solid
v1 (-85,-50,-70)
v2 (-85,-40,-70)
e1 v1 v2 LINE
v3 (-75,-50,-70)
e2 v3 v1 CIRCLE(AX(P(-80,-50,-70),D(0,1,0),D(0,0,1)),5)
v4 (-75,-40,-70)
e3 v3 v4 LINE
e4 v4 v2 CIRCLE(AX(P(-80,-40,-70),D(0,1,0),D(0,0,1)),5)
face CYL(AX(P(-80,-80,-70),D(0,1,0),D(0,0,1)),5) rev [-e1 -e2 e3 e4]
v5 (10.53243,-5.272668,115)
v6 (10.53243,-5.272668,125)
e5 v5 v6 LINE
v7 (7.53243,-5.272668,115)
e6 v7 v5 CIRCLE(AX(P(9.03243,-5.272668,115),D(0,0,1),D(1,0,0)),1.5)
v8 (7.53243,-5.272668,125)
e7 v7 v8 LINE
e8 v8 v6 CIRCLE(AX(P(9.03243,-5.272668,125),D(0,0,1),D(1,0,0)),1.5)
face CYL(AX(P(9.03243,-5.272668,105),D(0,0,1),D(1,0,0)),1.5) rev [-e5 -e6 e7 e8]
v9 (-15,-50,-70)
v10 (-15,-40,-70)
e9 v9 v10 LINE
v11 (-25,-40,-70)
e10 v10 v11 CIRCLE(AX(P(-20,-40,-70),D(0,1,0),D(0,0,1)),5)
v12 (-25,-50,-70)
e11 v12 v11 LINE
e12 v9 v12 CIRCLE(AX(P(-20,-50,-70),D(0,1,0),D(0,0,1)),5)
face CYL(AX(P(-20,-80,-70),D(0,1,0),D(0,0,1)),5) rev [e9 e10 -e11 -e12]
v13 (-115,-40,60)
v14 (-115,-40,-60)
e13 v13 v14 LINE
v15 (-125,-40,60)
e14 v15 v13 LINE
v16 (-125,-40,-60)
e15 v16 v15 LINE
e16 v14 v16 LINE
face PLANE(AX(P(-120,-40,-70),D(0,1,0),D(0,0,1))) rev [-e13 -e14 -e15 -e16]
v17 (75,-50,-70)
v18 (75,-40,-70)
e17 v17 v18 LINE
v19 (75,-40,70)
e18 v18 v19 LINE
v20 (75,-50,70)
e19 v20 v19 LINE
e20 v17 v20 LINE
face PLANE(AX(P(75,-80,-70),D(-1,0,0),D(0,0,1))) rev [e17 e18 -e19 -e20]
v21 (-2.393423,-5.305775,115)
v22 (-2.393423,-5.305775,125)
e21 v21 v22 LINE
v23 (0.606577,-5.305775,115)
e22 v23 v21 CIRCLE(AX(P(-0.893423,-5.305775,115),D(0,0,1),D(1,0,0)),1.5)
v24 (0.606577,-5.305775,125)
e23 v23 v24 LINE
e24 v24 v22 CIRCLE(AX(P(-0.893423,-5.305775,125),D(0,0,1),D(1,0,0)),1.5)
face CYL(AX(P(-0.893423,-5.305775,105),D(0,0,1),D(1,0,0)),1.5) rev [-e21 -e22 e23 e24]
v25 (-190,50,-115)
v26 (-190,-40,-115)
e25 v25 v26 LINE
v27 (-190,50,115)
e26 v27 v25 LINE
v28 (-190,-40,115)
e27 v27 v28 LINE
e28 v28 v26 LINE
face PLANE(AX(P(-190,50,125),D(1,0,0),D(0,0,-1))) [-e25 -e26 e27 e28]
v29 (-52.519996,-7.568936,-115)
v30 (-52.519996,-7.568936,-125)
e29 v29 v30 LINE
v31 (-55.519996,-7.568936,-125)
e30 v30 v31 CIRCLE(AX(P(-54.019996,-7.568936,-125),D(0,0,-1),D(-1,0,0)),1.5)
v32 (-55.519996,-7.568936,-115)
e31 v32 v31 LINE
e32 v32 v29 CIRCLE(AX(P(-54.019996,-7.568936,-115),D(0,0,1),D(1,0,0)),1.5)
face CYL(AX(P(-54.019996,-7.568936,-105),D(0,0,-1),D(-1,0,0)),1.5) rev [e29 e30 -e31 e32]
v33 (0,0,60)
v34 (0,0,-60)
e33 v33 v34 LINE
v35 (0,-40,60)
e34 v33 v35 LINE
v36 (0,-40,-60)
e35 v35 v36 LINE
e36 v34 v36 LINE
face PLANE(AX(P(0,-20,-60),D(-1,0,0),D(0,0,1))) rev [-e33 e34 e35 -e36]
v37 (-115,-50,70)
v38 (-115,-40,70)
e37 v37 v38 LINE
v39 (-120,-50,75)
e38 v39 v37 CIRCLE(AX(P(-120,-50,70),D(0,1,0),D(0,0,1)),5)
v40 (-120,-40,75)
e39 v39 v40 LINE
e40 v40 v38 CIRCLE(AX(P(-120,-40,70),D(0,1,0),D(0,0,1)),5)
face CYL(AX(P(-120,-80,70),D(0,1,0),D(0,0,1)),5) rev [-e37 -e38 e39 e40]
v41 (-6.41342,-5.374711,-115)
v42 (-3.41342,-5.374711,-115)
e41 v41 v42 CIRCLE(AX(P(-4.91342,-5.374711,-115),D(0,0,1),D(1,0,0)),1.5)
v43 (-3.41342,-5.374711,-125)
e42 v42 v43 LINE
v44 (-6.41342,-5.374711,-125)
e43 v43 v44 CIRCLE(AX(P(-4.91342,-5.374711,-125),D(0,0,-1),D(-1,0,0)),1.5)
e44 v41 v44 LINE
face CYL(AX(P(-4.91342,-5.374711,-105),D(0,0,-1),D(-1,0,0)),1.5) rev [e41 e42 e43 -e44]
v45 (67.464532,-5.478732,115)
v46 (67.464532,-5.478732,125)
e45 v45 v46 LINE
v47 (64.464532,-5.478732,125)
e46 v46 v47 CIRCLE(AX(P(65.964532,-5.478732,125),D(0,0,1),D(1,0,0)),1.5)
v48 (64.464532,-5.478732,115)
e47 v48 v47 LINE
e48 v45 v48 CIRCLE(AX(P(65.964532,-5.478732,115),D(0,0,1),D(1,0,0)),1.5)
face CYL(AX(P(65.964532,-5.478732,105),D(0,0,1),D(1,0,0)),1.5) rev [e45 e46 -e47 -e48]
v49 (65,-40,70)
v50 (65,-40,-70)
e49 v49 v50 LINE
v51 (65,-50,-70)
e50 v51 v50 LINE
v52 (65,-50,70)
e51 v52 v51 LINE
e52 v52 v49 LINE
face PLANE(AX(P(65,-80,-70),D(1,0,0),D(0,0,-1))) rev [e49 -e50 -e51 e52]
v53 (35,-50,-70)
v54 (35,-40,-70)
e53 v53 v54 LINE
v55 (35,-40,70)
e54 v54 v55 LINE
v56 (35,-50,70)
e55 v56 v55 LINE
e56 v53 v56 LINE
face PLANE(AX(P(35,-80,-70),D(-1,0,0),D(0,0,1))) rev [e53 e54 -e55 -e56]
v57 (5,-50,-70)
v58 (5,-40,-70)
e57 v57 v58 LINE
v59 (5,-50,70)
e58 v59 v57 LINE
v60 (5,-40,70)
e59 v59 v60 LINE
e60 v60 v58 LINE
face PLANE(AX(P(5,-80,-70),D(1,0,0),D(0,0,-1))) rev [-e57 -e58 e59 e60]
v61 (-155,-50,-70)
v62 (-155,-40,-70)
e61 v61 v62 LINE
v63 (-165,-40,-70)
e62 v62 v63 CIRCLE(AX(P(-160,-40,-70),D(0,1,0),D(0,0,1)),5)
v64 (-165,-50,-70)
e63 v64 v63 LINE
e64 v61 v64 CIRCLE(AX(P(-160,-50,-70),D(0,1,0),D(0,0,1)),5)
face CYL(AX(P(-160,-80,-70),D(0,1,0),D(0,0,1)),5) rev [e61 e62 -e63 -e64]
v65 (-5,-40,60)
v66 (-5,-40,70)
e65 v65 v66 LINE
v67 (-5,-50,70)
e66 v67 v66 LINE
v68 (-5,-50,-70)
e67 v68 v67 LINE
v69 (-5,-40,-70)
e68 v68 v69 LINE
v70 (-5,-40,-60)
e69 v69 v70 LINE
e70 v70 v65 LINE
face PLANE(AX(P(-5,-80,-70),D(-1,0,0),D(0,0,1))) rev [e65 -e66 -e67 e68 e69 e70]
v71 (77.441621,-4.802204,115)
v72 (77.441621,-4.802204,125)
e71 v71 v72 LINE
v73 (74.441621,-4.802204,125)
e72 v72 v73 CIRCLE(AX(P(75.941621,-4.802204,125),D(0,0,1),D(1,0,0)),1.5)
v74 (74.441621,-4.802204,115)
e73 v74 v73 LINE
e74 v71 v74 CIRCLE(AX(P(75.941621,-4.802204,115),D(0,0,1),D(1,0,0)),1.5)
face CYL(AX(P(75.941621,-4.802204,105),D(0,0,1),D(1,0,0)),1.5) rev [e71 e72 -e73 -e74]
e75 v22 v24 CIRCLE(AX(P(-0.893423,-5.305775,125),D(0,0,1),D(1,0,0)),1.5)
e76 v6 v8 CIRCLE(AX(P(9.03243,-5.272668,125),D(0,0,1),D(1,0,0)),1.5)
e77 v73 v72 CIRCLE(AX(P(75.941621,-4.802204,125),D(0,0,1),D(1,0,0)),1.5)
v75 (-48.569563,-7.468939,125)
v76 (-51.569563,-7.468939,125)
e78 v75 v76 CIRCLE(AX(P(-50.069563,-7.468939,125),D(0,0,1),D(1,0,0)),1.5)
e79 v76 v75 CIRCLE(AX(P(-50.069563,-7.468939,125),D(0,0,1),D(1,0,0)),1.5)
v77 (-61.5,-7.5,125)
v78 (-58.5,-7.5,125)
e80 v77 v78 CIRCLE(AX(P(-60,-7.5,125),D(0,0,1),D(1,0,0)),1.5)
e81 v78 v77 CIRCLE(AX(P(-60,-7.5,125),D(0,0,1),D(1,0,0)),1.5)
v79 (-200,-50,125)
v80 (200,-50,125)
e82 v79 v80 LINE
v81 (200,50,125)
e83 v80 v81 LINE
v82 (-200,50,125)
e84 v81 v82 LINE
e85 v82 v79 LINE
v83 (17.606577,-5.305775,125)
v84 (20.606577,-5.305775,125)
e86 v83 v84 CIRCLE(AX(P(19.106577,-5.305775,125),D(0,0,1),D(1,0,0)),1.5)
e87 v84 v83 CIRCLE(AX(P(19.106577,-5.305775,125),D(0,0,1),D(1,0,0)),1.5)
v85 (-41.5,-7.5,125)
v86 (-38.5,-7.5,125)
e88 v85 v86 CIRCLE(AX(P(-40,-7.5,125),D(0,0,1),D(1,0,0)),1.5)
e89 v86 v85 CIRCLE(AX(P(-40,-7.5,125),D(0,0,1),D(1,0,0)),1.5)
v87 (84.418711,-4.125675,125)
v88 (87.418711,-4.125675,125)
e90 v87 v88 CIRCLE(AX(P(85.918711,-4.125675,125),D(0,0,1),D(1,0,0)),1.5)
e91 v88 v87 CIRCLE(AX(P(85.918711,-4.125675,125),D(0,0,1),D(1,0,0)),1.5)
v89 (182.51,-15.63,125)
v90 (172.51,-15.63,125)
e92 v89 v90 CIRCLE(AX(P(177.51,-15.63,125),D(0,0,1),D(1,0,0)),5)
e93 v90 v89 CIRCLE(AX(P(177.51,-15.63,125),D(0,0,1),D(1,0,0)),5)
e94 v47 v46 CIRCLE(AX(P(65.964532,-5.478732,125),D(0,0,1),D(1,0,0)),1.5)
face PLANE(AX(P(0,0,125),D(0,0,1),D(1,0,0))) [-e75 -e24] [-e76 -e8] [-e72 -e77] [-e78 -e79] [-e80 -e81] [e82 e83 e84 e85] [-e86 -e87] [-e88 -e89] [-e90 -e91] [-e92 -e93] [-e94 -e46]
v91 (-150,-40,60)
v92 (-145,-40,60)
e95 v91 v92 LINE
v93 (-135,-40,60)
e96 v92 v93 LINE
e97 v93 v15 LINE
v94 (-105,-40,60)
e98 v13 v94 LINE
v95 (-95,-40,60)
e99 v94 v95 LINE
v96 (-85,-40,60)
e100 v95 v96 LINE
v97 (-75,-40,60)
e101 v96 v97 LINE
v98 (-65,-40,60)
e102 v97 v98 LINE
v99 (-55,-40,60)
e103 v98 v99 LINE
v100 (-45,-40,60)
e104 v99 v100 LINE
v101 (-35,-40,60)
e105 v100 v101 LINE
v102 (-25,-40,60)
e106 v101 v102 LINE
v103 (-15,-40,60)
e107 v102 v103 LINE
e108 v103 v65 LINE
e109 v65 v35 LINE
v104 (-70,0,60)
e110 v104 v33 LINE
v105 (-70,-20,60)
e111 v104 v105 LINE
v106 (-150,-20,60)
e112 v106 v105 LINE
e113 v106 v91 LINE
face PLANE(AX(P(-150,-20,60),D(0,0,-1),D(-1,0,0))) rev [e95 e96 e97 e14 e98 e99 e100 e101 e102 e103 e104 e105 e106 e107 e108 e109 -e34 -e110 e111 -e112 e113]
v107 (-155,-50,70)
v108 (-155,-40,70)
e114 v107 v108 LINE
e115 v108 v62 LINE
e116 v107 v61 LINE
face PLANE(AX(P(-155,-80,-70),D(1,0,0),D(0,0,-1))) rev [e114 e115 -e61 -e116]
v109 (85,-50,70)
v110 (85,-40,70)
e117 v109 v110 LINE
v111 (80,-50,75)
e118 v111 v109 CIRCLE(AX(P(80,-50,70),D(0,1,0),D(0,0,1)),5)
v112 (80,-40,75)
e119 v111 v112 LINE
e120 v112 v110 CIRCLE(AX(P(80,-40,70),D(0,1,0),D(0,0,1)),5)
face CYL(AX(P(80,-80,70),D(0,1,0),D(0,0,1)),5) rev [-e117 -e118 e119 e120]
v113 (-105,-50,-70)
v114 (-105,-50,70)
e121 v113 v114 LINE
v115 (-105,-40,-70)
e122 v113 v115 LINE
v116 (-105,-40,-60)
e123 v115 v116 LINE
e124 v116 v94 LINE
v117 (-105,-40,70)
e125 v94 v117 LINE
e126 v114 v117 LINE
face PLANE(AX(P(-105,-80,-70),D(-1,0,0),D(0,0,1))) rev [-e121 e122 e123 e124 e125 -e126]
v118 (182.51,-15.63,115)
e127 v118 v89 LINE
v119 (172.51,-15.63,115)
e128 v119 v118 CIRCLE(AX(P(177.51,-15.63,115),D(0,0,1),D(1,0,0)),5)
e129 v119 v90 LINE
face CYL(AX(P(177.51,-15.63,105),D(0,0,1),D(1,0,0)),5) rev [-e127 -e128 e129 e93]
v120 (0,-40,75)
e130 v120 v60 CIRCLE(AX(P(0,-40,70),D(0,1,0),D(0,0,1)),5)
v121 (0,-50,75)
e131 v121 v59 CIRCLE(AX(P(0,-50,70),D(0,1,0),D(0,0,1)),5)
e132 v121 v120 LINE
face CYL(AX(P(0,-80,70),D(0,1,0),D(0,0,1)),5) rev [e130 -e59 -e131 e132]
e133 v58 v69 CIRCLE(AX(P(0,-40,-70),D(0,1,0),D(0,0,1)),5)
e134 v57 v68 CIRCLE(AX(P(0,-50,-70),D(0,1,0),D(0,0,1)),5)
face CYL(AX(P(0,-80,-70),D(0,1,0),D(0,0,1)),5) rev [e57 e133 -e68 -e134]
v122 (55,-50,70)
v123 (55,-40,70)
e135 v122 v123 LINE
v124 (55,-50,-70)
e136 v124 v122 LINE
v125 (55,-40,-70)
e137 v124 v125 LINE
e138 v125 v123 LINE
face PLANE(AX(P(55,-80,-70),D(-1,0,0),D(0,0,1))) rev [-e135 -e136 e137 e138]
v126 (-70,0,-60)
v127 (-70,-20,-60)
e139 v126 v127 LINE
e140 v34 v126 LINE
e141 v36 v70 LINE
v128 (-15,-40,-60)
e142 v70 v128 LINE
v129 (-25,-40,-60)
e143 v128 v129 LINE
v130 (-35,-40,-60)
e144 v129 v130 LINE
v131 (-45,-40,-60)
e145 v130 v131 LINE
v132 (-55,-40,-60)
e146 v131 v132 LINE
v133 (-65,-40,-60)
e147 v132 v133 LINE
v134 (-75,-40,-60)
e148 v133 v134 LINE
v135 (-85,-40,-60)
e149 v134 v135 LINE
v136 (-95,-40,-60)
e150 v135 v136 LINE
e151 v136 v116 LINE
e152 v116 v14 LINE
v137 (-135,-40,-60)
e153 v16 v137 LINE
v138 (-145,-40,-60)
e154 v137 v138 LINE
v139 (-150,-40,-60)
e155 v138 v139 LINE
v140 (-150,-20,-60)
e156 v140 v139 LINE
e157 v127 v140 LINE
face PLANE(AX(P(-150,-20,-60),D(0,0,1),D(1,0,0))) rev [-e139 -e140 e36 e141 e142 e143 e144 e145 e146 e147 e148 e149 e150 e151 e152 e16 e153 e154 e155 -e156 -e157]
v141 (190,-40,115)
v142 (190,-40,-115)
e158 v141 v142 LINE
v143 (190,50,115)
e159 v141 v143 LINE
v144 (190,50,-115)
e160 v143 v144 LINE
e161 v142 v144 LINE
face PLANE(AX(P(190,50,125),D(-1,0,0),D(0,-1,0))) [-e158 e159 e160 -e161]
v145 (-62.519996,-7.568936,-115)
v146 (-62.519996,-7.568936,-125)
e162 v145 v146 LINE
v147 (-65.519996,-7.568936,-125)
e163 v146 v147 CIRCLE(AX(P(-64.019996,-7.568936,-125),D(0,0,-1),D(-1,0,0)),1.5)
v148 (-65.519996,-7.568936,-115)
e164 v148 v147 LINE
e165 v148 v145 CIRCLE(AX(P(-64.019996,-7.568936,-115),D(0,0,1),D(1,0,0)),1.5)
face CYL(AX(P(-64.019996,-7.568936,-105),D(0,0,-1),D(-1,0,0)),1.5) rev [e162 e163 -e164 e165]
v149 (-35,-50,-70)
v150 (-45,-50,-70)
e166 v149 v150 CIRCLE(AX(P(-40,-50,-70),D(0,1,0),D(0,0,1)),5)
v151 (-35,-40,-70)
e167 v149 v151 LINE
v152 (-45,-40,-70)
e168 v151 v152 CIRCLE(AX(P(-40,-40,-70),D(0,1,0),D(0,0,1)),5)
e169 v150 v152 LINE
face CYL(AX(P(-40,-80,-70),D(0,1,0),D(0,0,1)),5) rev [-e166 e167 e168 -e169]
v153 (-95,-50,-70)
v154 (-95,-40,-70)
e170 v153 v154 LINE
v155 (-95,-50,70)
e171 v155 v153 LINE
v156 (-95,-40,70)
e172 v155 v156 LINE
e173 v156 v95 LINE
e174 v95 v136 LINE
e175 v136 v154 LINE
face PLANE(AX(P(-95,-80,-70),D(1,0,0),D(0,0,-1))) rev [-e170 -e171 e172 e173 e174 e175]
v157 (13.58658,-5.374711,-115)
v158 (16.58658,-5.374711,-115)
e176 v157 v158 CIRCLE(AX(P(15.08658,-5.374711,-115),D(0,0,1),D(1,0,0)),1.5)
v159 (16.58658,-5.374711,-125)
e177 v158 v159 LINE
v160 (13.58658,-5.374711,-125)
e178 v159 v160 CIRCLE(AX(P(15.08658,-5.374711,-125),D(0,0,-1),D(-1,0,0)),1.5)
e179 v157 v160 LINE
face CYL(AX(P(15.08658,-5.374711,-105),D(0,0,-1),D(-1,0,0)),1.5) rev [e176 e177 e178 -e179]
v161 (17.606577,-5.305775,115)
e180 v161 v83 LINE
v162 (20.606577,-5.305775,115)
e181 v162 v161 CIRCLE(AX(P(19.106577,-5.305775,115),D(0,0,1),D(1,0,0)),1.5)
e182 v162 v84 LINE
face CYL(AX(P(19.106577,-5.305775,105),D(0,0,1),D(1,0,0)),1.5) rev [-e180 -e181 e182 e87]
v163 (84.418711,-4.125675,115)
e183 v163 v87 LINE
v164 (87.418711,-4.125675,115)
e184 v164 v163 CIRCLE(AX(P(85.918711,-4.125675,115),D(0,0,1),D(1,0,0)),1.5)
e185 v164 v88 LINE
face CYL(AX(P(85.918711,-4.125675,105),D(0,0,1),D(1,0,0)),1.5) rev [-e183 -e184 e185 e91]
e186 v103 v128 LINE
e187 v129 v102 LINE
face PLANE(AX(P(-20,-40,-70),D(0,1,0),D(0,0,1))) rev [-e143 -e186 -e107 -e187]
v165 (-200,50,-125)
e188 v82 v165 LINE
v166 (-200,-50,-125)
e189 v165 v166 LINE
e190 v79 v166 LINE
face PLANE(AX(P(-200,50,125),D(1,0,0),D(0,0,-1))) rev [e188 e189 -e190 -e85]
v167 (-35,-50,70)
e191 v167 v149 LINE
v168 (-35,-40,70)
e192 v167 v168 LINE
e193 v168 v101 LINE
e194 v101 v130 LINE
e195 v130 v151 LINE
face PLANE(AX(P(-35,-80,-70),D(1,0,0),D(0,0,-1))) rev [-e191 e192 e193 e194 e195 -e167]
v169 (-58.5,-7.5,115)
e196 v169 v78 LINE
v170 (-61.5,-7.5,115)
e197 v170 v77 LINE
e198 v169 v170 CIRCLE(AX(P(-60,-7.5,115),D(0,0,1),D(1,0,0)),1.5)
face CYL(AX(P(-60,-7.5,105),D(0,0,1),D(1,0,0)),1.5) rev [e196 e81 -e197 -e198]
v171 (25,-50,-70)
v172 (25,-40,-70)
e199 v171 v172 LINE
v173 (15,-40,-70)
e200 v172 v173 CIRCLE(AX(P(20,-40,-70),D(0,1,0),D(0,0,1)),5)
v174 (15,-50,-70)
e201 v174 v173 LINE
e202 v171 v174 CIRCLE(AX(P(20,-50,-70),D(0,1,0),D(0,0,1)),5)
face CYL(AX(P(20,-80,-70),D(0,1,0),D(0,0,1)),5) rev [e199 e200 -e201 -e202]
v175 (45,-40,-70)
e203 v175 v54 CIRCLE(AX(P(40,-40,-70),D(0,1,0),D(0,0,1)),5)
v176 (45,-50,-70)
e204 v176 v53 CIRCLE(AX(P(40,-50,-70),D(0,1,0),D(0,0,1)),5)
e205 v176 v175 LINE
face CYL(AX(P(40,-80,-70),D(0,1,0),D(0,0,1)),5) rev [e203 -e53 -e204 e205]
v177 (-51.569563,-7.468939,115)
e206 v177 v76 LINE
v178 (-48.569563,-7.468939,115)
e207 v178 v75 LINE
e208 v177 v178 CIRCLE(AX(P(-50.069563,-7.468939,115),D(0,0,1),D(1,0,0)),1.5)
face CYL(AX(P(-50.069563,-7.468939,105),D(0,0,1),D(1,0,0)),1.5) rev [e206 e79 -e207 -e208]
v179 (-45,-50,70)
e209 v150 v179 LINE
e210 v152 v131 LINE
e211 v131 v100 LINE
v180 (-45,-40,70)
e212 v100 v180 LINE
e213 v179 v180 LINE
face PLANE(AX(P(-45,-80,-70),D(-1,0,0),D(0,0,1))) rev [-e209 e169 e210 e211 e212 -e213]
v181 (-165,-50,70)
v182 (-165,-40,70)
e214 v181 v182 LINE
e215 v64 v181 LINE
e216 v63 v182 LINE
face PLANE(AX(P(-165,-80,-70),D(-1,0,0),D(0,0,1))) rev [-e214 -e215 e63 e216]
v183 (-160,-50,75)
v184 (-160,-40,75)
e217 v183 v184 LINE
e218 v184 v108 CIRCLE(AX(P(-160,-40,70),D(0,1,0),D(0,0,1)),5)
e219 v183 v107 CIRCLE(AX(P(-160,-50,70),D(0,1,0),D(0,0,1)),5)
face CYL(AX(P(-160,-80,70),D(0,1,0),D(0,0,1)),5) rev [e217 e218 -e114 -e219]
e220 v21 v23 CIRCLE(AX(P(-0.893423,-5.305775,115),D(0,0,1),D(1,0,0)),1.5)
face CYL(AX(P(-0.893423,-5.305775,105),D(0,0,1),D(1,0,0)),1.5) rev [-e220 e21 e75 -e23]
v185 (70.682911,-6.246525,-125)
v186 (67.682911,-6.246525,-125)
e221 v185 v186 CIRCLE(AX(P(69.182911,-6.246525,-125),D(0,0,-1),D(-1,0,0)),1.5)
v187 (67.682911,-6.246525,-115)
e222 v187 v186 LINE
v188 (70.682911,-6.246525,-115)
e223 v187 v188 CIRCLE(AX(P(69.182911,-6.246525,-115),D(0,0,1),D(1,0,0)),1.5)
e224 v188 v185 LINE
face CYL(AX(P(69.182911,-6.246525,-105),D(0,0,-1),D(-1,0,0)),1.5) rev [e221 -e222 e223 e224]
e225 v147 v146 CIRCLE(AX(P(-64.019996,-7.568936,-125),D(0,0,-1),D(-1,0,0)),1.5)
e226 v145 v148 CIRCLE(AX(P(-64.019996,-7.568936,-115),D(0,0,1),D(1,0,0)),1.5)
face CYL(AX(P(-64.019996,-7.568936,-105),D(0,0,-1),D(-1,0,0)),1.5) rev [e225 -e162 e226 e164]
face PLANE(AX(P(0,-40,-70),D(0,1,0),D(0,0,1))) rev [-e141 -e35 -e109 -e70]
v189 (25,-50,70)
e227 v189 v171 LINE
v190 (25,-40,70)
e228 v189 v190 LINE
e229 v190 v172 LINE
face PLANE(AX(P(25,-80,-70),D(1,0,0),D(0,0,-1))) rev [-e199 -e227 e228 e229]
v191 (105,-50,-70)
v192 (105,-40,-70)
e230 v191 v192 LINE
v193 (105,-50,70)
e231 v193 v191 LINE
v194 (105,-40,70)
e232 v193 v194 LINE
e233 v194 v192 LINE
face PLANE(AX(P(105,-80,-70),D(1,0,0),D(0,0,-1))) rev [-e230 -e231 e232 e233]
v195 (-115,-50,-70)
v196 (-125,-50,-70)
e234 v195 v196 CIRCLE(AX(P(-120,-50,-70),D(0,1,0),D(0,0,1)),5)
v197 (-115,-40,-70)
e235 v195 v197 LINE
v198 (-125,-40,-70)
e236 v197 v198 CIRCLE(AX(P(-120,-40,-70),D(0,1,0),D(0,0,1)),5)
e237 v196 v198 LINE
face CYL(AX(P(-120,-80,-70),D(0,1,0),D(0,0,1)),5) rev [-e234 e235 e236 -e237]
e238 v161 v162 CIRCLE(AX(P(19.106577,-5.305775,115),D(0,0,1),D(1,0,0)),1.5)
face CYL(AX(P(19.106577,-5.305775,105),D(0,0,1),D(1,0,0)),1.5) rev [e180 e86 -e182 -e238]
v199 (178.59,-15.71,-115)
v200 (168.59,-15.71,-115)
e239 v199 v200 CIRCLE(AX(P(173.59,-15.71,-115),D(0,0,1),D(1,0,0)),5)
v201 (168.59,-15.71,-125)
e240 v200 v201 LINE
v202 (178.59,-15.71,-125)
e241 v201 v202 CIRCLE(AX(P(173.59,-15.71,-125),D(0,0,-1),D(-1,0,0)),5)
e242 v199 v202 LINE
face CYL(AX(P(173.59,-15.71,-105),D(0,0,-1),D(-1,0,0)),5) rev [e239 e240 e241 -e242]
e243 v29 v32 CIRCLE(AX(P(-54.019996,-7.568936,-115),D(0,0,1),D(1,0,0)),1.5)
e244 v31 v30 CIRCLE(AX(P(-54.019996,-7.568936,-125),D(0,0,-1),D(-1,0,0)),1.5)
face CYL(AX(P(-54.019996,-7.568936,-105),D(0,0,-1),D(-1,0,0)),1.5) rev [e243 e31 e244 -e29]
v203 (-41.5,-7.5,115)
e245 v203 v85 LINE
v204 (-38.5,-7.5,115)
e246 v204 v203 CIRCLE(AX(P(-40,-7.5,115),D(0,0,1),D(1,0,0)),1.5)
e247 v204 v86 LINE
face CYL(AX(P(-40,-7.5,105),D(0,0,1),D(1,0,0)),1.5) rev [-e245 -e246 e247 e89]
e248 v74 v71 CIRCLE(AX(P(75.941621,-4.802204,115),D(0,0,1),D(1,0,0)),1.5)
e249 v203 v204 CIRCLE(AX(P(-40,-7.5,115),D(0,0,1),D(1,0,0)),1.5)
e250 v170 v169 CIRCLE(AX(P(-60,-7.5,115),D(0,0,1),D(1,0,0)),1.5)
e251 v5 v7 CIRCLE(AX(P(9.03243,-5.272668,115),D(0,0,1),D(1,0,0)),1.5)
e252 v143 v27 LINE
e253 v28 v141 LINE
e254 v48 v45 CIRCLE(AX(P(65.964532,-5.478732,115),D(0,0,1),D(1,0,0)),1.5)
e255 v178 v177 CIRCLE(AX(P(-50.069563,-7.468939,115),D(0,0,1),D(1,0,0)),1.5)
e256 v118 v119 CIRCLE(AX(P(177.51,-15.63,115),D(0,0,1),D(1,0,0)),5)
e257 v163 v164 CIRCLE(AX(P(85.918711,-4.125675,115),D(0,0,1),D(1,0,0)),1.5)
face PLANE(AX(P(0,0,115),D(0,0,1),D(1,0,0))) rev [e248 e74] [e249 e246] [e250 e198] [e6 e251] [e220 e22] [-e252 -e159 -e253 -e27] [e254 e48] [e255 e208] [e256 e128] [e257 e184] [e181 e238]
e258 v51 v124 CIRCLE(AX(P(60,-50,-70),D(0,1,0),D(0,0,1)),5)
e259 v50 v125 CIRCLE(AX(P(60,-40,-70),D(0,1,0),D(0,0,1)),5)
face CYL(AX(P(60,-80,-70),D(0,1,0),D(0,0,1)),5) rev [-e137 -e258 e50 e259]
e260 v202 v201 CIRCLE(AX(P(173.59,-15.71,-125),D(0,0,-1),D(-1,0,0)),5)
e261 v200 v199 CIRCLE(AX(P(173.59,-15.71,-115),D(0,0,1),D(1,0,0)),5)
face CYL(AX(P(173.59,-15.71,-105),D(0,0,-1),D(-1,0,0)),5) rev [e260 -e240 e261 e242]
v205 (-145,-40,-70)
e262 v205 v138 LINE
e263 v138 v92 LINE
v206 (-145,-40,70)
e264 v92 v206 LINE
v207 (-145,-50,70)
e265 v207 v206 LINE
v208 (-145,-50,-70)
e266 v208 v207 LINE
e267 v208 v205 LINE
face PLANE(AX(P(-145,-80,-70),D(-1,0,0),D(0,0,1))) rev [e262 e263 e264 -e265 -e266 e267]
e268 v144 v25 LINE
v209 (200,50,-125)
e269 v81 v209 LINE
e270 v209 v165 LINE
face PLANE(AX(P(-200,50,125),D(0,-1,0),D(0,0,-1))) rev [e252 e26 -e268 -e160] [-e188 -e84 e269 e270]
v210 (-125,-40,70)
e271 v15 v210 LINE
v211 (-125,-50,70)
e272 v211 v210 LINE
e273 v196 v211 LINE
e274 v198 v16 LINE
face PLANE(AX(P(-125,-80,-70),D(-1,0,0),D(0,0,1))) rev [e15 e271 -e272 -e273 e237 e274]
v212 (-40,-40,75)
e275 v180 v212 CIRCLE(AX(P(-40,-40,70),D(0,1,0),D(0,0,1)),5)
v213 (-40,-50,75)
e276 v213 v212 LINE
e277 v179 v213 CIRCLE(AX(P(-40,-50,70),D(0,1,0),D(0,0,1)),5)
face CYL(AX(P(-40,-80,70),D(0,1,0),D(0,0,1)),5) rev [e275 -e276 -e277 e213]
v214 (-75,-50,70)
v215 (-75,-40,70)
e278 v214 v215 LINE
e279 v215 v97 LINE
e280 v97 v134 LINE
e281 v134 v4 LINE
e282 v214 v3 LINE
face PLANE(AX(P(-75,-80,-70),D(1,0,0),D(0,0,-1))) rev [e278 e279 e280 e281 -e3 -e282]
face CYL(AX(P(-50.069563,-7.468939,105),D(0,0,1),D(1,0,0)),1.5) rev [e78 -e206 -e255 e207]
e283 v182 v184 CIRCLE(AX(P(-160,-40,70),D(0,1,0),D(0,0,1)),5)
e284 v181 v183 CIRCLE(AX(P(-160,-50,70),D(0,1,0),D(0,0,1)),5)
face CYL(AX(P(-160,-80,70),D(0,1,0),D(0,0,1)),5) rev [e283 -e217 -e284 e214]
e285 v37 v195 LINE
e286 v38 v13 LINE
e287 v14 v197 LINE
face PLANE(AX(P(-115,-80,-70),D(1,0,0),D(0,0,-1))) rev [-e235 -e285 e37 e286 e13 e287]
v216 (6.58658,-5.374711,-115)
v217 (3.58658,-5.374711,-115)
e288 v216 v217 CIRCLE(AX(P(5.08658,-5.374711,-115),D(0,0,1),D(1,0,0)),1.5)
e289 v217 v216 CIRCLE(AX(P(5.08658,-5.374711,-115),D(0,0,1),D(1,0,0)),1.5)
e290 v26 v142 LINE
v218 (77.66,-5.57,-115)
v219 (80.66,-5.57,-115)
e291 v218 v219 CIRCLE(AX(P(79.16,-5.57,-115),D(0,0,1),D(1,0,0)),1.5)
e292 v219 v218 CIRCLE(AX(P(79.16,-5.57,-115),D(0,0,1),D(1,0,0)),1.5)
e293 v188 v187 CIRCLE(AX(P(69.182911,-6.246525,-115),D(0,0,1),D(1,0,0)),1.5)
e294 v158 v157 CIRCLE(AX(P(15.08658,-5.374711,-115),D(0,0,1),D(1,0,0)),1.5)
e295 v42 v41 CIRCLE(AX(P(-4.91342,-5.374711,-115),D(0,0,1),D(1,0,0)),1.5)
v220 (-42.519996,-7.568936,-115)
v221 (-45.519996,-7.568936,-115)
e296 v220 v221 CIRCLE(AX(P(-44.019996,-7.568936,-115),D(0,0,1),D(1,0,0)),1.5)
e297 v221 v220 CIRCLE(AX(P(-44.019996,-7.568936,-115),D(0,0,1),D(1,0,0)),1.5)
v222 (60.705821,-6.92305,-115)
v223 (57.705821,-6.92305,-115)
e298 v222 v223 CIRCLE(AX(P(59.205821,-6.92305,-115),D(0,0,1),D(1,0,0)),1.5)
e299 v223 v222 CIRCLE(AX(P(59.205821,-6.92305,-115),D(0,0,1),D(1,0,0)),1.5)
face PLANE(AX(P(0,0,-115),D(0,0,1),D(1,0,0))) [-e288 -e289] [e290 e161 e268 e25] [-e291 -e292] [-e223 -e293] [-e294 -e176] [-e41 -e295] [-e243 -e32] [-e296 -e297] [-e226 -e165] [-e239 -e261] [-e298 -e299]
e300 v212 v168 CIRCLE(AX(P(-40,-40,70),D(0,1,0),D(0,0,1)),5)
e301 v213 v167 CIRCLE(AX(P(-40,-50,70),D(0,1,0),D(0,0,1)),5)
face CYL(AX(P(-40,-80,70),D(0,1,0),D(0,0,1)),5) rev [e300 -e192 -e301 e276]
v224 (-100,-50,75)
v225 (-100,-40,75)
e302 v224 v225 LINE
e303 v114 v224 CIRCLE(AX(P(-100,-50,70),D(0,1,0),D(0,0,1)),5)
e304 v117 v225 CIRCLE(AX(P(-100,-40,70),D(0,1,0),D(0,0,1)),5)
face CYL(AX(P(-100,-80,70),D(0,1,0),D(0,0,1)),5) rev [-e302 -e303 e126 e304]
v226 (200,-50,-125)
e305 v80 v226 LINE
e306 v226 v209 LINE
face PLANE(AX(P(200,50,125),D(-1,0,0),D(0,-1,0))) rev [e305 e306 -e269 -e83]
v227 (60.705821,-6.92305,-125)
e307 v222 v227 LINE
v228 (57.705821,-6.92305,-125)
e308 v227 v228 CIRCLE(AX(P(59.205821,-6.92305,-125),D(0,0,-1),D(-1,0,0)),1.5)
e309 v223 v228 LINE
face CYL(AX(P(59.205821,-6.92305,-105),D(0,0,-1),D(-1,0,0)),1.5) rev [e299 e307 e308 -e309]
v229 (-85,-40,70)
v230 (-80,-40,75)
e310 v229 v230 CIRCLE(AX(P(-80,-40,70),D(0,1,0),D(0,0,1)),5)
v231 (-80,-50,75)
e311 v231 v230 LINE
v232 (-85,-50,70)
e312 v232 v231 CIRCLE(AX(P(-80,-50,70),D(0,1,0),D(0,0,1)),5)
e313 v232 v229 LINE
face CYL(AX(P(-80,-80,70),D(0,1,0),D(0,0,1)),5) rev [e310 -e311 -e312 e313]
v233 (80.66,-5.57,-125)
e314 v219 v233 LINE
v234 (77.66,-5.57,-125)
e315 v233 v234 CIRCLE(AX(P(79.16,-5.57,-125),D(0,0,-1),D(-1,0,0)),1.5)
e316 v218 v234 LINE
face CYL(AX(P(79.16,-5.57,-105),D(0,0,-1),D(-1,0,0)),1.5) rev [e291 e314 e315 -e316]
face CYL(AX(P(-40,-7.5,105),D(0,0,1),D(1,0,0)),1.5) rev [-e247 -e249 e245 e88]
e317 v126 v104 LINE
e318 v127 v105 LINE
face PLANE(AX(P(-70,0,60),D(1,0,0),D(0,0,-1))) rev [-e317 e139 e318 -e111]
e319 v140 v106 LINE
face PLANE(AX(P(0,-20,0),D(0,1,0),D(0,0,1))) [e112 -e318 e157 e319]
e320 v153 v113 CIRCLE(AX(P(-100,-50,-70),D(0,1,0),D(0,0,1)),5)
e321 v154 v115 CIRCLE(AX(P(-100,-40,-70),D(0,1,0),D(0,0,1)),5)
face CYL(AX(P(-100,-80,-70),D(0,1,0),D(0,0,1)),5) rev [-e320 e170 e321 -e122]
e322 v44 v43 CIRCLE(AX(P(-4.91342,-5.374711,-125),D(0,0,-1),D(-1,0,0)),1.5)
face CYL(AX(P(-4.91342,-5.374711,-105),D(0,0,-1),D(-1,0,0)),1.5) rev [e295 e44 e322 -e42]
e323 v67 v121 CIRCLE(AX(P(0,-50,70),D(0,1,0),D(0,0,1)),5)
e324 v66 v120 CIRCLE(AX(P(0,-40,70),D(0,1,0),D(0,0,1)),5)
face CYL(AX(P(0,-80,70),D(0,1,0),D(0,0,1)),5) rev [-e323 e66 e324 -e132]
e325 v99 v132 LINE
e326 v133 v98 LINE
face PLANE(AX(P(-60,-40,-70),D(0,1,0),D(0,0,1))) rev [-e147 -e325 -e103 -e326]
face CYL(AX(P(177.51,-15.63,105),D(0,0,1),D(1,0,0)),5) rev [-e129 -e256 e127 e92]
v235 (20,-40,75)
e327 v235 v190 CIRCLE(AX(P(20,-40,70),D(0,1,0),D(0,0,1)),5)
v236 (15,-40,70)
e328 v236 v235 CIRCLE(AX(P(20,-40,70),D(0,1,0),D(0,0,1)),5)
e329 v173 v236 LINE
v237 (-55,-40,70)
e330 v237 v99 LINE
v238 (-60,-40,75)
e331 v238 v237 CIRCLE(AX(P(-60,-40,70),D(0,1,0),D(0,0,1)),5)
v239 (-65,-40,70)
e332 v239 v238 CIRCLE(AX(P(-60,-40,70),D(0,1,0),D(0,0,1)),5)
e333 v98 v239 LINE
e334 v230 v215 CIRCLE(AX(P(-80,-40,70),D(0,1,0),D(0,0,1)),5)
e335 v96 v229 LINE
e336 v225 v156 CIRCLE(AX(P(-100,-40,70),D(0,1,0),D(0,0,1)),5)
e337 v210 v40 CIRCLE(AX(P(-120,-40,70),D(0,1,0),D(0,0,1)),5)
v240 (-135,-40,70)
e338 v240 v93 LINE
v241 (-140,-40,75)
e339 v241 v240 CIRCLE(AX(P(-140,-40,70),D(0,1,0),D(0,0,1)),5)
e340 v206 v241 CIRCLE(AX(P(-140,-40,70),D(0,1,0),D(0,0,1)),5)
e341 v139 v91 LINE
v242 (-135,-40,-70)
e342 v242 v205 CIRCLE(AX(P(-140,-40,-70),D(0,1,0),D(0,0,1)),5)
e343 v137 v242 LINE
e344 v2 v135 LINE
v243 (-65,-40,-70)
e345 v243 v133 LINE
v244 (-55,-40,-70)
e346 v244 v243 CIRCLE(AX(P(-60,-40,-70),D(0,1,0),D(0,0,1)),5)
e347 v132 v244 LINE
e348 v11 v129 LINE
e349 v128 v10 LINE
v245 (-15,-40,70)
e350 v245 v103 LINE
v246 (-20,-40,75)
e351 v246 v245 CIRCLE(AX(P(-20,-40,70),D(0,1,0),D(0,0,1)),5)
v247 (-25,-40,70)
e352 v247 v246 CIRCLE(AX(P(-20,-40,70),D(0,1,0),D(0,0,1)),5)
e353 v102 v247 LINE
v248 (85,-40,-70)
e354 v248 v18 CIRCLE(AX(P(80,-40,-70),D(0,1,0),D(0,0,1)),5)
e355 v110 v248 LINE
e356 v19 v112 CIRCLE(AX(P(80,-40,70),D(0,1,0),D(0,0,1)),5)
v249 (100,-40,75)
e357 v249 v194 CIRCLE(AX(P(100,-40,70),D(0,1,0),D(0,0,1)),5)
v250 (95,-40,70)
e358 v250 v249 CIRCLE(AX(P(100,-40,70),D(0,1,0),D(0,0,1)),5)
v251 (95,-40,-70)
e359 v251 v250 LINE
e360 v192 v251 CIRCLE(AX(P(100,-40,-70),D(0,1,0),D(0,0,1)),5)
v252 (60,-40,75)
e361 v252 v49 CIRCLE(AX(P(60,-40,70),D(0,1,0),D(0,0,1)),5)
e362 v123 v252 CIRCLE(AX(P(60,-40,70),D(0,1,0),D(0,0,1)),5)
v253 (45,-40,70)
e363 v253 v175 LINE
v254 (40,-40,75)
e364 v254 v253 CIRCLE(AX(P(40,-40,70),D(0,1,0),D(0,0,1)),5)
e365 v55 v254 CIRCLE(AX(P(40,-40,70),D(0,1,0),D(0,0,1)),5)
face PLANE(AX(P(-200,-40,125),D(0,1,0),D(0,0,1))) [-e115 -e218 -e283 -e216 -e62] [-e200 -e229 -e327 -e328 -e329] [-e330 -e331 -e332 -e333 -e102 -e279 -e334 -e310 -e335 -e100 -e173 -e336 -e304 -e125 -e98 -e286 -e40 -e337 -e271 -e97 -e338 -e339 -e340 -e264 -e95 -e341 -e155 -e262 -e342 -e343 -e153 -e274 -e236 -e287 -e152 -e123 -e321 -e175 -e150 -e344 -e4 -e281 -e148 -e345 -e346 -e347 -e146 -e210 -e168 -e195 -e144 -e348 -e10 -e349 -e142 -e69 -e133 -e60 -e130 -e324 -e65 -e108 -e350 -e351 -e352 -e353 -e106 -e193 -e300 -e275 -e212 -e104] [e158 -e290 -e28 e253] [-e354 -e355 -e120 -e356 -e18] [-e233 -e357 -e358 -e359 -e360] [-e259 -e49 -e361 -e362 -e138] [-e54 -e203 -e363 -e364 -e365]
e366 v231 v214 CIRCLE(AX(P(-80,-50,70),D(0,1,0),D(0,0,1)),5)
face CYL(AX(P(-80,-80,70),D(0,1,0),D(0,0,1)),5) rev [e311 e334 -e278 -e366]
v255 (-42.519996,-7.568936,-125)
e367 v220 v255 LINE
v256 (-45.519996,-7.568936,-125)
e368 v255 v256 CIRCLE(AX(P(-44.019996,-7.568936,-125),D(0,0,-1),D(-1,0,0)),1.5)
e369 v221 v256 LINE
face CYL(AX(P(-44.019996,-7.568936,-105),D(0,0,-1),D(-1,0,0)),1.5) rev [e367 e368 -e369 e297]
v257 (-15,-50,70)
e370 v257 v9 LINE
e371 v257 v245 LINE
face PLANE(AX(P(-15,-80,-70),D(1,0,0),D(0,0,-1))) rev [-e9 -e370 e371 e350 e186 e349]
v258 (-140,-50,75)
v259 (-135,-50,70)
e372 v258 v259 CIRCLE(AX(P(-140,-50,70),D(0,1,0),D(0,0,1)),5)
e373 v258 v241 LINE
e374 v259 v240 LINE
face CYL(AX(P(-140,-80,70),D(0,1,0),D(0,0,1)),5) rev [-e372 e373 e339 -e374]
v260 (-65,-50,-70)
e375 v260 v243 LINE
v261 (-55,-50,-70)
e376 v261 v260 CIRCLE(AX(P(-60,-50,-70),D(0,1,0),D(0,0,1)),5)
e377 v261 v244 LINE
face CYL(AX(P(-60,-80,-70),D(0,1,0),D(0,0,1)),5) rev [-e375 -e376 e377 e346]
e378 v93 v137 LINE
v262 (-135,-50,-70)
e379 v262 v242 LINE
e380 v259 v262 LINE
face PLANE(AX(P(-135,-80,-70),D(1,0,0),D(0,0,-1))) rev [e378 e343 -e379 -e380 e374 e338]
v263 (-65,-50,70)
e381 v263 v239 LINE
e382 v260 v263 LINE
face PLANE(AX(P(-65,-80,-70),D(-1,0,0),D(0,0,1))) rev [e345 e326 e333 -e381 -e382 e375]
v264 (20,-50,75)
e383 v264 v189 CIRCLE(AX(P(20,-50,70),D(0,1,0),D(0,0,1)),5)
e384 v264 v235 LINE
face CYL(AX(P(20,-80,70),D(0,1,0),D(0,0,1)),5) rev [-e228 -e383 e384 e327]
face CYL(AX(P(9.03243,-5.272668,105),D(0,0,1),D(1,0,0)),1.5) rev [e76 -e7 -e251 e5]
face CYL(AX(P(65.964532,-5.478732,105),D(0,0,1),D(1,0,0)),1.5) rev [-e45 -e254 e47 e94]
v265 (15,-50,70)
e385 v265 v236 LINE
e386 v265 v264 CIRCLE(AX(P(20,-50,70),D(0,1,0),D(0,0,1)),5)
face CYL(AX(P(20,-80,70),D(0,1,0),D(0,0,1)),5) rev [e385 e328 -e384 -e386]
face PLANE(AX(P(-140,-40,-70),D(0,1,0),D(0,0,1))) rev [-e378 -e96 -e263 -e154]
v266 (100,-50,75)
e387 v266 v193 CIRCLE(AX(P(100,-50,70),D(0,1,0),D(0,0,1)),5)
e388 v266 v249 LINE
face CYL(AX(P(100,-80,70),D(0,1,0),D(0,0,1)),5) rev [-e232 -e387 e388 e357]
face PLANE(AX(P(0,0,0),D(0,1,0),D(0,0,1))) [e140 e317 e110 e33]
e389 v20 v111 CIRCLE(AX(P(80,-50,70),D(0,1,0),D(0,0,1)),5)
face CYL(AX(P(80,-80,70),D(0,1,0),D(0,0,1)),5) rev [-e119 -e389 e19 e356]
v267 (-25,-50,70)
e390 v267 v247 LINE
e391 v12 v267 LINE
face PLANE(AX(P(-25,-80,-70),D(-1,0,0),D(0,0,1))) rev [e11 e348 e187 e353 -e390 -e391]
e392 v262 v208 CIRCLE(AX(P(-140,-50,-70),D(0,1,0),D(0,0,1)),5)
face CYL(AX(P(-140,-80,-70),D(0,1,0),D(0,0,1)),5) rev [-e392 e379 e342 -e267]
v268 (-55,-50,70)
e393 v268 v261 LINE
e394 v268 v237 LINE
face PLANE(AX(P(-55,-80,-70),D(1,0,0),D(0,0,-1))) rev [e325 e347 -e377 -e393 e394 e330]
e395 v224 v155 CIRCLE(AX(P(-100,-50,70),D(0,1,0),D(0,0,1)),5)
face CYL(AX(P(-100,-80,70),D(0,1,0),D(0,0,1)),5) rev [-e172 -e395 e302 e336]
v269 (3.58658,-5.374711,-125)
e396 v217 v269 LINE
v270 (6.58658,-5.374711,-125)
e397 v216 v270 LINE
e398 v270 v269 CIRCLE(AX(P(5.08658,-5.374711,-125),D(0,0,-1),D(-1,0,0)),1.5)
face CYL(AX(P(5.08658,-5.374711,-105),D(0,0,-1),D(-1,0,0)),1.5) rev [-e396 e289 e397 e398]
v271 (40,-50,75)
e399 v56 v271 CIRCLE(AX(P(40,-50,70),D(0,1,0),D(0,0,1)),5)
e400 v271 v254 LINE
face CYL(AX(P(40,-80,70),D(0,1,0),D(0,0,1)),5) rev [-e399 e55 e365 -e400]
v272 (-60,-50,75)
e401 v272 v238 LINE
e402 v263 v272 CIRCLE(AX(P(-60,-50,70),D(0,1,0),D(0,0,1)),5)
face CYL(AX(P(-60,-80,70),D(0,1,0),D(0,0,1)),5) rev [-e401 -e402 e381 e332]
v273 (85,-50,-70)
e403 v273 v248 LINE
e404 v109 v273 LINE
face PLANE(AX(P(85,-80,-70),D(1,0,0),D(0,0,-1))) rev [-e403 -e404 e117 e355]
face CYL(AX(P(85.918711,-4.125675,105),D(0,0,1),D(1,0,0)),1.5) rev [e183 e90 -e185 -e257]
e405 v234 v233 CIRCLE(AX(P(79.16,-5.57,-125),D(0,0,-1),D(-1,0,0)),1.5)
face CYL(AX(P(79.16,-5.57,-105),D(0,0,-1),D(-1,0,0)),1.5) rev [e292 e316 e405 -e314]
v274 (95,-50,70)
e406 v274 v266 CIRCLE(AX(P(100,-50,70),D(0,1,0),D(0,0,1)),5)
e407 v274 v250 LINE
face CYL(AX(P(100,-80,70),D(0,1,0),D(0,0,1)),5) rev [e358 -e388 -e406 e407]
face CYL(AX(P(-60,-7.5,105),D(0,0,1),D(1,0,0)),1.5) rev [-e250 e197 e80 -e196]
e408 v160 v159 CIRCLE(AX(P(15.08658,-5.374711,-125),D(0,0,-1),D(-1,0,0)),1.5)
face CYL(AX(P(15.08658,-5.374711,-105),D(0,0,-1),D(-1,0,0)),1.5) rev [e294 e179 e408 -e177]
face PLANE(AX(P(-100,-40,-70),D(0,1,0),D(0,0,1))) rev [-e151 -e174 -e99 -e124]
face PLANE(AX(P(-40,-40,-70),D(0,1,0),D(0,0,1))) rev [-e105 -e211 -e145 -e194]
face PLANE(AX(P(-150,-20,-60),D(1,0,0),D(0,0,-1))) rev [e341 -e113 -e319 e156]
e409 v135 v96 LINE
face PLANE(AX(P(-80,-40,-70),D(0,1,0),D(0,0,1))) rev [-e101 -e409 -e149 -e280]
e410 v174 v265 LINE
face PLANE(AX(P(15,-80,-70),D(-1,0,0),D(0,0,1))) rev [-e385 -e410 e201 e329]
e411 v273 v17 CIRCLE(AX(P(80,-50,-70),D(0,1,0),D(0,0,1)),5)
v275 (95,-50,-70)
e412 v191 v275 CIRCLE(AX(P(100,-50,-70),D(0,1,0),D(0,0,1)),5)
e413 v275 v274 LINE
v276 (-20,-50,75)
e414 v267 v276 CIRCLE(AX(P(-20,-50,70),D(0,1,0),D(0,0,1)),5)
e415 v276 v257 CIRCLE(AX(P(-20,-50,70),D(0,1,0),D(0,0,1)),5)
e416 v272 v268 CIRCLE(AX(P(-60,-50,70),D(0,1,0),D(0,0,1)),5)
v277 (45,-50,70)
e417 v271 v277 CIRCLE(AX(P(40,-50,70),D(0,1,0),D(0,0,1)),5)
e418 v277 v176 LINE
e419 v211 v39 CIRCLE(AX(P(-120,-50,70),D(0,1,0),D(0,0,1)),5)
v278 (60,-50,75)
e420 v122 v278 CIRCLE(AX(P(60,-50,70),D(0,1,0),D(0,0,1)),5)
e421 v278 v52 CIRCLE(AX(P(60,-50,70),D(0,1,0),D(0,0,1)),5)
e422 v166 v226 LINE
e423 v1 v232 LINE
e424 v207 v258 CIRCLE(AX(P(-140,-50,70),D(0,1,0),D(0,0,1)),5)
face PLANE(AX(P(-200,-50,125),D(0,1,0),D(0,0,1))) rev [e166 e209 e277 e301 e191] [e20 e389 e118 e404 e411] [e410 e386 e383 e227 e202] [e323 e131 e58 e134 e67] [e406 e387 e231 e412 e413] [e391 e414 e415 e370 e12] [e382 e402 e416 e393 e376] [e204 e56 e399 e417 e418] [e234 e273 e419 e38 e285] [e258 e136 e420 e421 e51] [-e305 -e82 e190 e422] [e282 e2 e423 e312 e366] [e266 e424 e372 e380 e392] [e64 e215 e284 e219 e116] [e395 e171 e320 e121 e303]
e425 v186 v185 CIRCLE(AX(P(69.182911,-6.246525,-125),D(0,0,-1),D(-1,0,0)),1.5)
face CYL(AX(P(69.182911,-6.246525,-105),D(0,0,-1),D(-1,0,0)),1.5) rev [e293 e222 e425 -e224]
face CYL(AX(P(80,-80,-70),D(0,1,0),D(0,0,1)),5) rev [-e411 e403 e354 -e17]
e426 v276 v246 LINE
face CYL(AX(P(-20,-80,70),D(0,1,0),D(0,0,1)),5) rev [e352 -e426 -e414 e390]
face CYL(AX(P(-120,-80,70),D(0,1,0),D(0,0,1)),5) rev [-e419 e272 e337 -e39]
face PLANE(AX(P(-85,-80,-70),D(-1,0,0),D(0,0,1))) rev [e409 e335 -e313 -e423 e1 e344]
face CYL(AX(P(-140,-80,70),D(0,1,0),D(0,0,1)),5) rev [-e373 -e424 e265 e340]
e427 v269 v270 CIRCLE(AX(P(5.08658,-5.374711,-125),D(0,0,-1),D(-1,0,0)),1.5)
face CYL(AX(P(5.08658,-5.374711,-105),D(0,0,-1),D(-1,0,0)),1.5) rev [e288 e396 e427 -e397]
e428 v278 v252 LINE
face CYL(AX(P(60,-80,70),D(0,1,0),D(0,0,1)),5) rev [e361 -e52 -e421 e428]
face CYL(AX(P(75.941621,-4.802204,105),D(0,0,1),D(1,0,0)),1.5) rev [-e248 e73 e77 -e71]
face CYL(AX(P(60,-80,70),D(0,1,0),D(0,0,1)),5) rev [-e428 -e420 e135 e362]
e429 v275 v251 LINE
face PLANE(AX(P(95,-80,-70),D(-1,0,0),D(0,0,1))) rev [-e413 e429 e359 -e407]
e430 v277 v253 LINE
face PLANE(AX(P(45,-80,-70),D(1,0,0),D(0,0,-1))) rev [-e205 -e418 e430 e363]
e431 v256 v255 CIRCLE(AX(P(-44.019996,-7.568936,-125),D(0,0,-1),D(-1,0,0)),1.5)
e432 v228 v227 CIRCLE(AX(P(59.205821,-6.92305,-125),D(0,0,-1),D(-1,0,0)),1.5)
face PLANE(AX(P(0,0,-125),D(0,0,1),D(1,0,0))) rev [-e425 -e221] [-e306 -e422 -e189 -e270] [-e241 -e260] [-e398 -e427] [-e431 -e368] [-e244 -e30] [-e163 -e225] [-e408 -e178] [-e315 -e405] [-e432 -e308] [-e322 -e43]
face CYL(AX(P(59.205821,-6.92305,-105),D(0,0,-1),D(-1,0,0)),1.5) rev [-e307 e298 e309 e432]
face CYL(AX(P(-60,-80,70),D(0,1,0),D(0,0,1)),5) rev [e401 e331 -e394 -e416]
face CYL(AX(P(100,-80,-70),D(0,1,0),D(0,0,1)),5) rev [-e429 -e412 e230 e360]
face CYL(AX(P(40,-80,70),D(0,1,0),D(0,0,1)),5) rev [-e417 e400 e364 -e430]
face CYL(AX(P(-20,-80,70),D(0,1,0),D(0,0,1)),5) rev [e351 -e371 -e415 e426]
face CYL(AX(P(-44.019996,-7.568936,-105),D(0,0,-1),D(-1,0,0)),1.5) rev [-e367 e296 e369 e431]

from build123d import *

# Parameters (mm, degrees)
SKETCH1_W           = 400
SKETCH1_H           = 100
BOSS_EXTRUDE1_DEPTH = 125
SHELL1_T            = -10
SKETCH2_R           = 1.5
CUT_EXTRUDE1_DEPTH  = 20
SKETCH6_W           = 150
SKETCH6_H           = 120
BOSS_EXTRUDE2_DEPTH = 20
CUT_EXTRUDE4_DEPTH  = 40
SKETCH10_W          = 70
SKETCH10_H          = 120
BOSS_EXTRUDE4_DEPTH = 20
SKETCH11_R          = 5
CUT_EXTRUDE5_DEPTH  = 20
SKETCH12_R          = 5
CUT_EXTRUDE6_DEPTH  = 20
SKETCH13_R          = 1.5
CUT_EXTRUDE7_DEPTH  = 20


with BuildPart() as part:
    # Sketch1 → Boss-Extrude1 (new, symmetric)
    with BuildSketch(Plane.XY):
        Rectangle(SKETCH1_W, SKETCH1_H)
    extrude(amount=BOSS_EXTRUDE1_DEPTH, both=True)

    # Shell1
    shell1_openings = [part.faces().sort_by_distance(p)[0] for p in [
        (0, 50, 0),
    ]]
    offset(amount=SHELL1_T, openings=shell1_openings, kind=Kind.INTERSECTION)

    # Sketch2 → Cut-Extrude1 (cut)
    with BuildSketch(Plane.XY.offset(125)):
        with Locations((-60, -7.5)):
            Circle(SKETCH2_R)
        with Locations((-50.069563203, -7.468939407)):
            Circle(SKETCH2_R)
        with Locations((-40, -7.499999981)):
            Circle(SKETCH2_R)
        with Locations((-0.893423466, -5.30577502)):
            Circle(SKETCH2_R)
        with Locations((9.032429625, -5.272668135)):
            Circle(SKETCH2_R)
        with Locations((19.106576534, -5.305775001)):
            Circle(SKETCH2_R)
        with Locations((65.964532087, -5.478731969)):
            Circle(SKETCH2_R)
        with Locations((75.941621303, -4.802203506)):
            Circle(SKETCH2_R)
        with Locations((85.91871052, -4.125675044)):
            Circle(SKETCH2_R)
    extrude(amount=-CUT_EXTRUDE1_DEPTH, mode=Mode.SUBTRACT)

    # Sketch6 → Boss-Extrude2 (add)
    with BuildSketch(Plane(origin=(0, -40, 0), x_dir=(1, 0, 0), z_dir=(0, 1, 0))):
        with Locations((-75, 0)):
            Rectangle(SKETCH6_W, SKETCH6_H)
    extrude(amount=BOSS_EXTRUDE2_DEPTH)

    # Sketch9 → Cut-Extrude4 (cut)
    with BuildSketch(Plane(origin=(0, -40, 0), x_dir=(1, 0, 0), z_dir=(0, 1, 0))):
        with BuildLine():
            Line((105, 70), (105, -70))
            ThreePointArc((105, -70), (100, -75), (95, -70))
            Line((95, -70), (95, 70))
            ThreePointArc((95, 70), (100, 75), (105, 70))
        make_face()
        with BuildLine():
            Line((85, 70), (85, -70))
            ThreePointArc((85, -70), (80, -75), (75, -70))
            Line((75, -70), (75, 70))
            ThreePointArc((75, 70), (80, 75), (85, 70))
        make_face()
        with BuildLine():
            Line((65, 70), (65, -70))
            ThreePointArc((65, -70), (60, -75), (55, -70))
            Line((55, -70), (55, 70))
            ThreePointArc((55, 70), (60, 75), (65, 70))
        make_face()
        with BuildLine():
            Line((45, 70), (45, -70))
            ThreePointArc((45, -70), (40, -75), (35, -70))
            Line((35, -70), (35, 70))
            ThreePointArc((35, 70), (40, 75), (45, 70))
        make_face()
        with BuildLine():
            Line((25, 70), (25, -70))
            ThreePointArc((25, -70), (20, -75), (15, -70))
            Line((15, -70), (15, 70))
            ThreePointArc((15, 70), (20, 75), (25, 70))
        make_face()
        with BuildLine():
            Line((5, 70), (5, -70))
            ThreePointArc((5, -70), (0, -75), (-5, -70))
            Line((-5, -70), (-5, 70))
            ThreePointArc((-5, 70), (0, 75), (5, 70))
        make_face()
        with BuildLine():
            Line((-15, 70), (-15, -70))
            ThreePointArc((-15, -70), (-20, -75), (-25, -70))
            Line((-25, -70), (-25, 70))
            ThreePointArc((-25, 70), (-20, 75), (-15, 70))
        make_face()
        with BuildLine():
            Line((-35, 70), (-35, -70))
            ThreePointArc((-35, -70), (-40, -75), (-45, -70))
            Line((-45, -70), (-45, 70))
            ThreePointArc((-45, 70), (-40, 75), (-35, 70))
        make_face()
        with BuildLine():
            Line((-55, 70), (-55, -70))
            ThreePointArc((-55, -70), (-60, -75), (-65, -70))
            Line((-65, -70), (-65, 70))
            ThreePointArc((-65, 70), (-60, 75), (-55, 70))
        make_face()
        with BuildLine():
            Line((-75, 70), (-75, -70))
            ThreePointArc((-75, -70), (-80, -75), (-85, -70))
            Line((-85, -70), (-85, 70))
            ThreePointArc((-85, 70), (-80, 75), (-75, 70))
        make_face()
        with BuildLine():
            Line((-95, 70), (-95, -70))
            ThreePointArc((-95, -70), (-100, -75), (-105, -70))
            Line((-105, -70), (-105, 70))
            ThreePointArc((-105, 70), (-100, 75), (-95, 70))
        make_face()
        with BuildLine():
            Line((-115, 70), (-115, -70))
            ThreePointArc((-115, -70), (-120, -75), (-125, -70))
            Line((-125, -70), (-125, 70))
            ThreePointArc((-125, 70), (-120, 75), (-115, 70))
        make_face()
        with BuildLine():
            Line((-135, 70), (-135, -70))
            ThreePointArc((-135, -70), (-140, -75), (-145, -70))
            Line((-145, -70), (-145, 70))
            ThreePointArc((-145, 70), (-140, 75), (-135, 70))
        make_face()
        with BuildLine():
            Line((-155, 70), (-155, -70))
            ThreePointArc((-155, -70), (-160, -75), (-165, -70))
            Line((-165, -70), (-165, 70))
            ThreePointArc((-165, 70), (-160, 75), (-155, 70))
        make_face()
    extrude(amount=-CUT_EXTRUDE4_DEPTH, mode=Mode.SUBTRACT)

    # Sketch10 → Boss-Extrude4 (add)
    with BuildSketch(Plane(origin=(0, -20, 0), x_dir=(1, 0, 0), z_dir=(0, 1, 0))):
        with Locations((-35, 0)):
            Rectangle(SKETCH10_W, SKETCH10_H)
    extrude(amount=BOSS_EXTRUDE4_DEPTH)

    # Sketch11 → Cut-Extrude5 (cut)
    with BuildSketch(Plane.XY.offset(125)):
        with Locations((177.51, -15.63)):
            Circle(SKETCH11_R)
    extrude(amount=-CUT_EXTRUDE5_DEPTH, mode=Mode.SUBTRACT)

    # Sketch12 → Cut-Extrude6 (cut)
    with BuildSketch(Plane(origin=(0, 0, -125), x_dir=(-1, 0, 0), z_dir=(0, 0, -1))):
        with Locations((-173.59, -15.71)):
            Circle(SKETCH12_R)
    extrude(amount=-CUT_EXTRUDE6_DEPTH, mode=Mode.SUBTRACT)

    # Sketch13 → Cut-Extrude7 (cut)
    with BuildSketch(Plane(origin=(0, 0, -125), x_dir=(-1, 0, 0), z_dir=(0, 0, -1))):
        with Locations((-79.16, -5.57)):
            Circle(SKETCH13_R)
        with Locations((-59.205821103, -6.923050088)):
            Circle(SKETCH13_R)
        with Locations((-69.182910551, -6.246525044)):
            Circle(SKETCH13_R)
        with Locations((64.01999621, -7.568935655)):
            Circle(SKETCH13_R)
        with Locations((54.01999621, -7.568935655)):
            Circle(SKETCH13_R)
        with Locations((44.01999621, -7.568935655)):
            Circle(SKETCH13_R)
        with Locations((4.913420159, -5.374710514)):
            Circle(SKETCH13_R)
        with Locations((-5.086579841, -5.374710514)):
            Circle(SKETCH13_R)
        with Locations((-15.086579841, -5.374710514)):
            Circle(SKETCH13_R)
    extrude(amount=-CUT_EXTRUDE7_DEPTH, mode=Mode.SUBTRACT)


solid = part.part
